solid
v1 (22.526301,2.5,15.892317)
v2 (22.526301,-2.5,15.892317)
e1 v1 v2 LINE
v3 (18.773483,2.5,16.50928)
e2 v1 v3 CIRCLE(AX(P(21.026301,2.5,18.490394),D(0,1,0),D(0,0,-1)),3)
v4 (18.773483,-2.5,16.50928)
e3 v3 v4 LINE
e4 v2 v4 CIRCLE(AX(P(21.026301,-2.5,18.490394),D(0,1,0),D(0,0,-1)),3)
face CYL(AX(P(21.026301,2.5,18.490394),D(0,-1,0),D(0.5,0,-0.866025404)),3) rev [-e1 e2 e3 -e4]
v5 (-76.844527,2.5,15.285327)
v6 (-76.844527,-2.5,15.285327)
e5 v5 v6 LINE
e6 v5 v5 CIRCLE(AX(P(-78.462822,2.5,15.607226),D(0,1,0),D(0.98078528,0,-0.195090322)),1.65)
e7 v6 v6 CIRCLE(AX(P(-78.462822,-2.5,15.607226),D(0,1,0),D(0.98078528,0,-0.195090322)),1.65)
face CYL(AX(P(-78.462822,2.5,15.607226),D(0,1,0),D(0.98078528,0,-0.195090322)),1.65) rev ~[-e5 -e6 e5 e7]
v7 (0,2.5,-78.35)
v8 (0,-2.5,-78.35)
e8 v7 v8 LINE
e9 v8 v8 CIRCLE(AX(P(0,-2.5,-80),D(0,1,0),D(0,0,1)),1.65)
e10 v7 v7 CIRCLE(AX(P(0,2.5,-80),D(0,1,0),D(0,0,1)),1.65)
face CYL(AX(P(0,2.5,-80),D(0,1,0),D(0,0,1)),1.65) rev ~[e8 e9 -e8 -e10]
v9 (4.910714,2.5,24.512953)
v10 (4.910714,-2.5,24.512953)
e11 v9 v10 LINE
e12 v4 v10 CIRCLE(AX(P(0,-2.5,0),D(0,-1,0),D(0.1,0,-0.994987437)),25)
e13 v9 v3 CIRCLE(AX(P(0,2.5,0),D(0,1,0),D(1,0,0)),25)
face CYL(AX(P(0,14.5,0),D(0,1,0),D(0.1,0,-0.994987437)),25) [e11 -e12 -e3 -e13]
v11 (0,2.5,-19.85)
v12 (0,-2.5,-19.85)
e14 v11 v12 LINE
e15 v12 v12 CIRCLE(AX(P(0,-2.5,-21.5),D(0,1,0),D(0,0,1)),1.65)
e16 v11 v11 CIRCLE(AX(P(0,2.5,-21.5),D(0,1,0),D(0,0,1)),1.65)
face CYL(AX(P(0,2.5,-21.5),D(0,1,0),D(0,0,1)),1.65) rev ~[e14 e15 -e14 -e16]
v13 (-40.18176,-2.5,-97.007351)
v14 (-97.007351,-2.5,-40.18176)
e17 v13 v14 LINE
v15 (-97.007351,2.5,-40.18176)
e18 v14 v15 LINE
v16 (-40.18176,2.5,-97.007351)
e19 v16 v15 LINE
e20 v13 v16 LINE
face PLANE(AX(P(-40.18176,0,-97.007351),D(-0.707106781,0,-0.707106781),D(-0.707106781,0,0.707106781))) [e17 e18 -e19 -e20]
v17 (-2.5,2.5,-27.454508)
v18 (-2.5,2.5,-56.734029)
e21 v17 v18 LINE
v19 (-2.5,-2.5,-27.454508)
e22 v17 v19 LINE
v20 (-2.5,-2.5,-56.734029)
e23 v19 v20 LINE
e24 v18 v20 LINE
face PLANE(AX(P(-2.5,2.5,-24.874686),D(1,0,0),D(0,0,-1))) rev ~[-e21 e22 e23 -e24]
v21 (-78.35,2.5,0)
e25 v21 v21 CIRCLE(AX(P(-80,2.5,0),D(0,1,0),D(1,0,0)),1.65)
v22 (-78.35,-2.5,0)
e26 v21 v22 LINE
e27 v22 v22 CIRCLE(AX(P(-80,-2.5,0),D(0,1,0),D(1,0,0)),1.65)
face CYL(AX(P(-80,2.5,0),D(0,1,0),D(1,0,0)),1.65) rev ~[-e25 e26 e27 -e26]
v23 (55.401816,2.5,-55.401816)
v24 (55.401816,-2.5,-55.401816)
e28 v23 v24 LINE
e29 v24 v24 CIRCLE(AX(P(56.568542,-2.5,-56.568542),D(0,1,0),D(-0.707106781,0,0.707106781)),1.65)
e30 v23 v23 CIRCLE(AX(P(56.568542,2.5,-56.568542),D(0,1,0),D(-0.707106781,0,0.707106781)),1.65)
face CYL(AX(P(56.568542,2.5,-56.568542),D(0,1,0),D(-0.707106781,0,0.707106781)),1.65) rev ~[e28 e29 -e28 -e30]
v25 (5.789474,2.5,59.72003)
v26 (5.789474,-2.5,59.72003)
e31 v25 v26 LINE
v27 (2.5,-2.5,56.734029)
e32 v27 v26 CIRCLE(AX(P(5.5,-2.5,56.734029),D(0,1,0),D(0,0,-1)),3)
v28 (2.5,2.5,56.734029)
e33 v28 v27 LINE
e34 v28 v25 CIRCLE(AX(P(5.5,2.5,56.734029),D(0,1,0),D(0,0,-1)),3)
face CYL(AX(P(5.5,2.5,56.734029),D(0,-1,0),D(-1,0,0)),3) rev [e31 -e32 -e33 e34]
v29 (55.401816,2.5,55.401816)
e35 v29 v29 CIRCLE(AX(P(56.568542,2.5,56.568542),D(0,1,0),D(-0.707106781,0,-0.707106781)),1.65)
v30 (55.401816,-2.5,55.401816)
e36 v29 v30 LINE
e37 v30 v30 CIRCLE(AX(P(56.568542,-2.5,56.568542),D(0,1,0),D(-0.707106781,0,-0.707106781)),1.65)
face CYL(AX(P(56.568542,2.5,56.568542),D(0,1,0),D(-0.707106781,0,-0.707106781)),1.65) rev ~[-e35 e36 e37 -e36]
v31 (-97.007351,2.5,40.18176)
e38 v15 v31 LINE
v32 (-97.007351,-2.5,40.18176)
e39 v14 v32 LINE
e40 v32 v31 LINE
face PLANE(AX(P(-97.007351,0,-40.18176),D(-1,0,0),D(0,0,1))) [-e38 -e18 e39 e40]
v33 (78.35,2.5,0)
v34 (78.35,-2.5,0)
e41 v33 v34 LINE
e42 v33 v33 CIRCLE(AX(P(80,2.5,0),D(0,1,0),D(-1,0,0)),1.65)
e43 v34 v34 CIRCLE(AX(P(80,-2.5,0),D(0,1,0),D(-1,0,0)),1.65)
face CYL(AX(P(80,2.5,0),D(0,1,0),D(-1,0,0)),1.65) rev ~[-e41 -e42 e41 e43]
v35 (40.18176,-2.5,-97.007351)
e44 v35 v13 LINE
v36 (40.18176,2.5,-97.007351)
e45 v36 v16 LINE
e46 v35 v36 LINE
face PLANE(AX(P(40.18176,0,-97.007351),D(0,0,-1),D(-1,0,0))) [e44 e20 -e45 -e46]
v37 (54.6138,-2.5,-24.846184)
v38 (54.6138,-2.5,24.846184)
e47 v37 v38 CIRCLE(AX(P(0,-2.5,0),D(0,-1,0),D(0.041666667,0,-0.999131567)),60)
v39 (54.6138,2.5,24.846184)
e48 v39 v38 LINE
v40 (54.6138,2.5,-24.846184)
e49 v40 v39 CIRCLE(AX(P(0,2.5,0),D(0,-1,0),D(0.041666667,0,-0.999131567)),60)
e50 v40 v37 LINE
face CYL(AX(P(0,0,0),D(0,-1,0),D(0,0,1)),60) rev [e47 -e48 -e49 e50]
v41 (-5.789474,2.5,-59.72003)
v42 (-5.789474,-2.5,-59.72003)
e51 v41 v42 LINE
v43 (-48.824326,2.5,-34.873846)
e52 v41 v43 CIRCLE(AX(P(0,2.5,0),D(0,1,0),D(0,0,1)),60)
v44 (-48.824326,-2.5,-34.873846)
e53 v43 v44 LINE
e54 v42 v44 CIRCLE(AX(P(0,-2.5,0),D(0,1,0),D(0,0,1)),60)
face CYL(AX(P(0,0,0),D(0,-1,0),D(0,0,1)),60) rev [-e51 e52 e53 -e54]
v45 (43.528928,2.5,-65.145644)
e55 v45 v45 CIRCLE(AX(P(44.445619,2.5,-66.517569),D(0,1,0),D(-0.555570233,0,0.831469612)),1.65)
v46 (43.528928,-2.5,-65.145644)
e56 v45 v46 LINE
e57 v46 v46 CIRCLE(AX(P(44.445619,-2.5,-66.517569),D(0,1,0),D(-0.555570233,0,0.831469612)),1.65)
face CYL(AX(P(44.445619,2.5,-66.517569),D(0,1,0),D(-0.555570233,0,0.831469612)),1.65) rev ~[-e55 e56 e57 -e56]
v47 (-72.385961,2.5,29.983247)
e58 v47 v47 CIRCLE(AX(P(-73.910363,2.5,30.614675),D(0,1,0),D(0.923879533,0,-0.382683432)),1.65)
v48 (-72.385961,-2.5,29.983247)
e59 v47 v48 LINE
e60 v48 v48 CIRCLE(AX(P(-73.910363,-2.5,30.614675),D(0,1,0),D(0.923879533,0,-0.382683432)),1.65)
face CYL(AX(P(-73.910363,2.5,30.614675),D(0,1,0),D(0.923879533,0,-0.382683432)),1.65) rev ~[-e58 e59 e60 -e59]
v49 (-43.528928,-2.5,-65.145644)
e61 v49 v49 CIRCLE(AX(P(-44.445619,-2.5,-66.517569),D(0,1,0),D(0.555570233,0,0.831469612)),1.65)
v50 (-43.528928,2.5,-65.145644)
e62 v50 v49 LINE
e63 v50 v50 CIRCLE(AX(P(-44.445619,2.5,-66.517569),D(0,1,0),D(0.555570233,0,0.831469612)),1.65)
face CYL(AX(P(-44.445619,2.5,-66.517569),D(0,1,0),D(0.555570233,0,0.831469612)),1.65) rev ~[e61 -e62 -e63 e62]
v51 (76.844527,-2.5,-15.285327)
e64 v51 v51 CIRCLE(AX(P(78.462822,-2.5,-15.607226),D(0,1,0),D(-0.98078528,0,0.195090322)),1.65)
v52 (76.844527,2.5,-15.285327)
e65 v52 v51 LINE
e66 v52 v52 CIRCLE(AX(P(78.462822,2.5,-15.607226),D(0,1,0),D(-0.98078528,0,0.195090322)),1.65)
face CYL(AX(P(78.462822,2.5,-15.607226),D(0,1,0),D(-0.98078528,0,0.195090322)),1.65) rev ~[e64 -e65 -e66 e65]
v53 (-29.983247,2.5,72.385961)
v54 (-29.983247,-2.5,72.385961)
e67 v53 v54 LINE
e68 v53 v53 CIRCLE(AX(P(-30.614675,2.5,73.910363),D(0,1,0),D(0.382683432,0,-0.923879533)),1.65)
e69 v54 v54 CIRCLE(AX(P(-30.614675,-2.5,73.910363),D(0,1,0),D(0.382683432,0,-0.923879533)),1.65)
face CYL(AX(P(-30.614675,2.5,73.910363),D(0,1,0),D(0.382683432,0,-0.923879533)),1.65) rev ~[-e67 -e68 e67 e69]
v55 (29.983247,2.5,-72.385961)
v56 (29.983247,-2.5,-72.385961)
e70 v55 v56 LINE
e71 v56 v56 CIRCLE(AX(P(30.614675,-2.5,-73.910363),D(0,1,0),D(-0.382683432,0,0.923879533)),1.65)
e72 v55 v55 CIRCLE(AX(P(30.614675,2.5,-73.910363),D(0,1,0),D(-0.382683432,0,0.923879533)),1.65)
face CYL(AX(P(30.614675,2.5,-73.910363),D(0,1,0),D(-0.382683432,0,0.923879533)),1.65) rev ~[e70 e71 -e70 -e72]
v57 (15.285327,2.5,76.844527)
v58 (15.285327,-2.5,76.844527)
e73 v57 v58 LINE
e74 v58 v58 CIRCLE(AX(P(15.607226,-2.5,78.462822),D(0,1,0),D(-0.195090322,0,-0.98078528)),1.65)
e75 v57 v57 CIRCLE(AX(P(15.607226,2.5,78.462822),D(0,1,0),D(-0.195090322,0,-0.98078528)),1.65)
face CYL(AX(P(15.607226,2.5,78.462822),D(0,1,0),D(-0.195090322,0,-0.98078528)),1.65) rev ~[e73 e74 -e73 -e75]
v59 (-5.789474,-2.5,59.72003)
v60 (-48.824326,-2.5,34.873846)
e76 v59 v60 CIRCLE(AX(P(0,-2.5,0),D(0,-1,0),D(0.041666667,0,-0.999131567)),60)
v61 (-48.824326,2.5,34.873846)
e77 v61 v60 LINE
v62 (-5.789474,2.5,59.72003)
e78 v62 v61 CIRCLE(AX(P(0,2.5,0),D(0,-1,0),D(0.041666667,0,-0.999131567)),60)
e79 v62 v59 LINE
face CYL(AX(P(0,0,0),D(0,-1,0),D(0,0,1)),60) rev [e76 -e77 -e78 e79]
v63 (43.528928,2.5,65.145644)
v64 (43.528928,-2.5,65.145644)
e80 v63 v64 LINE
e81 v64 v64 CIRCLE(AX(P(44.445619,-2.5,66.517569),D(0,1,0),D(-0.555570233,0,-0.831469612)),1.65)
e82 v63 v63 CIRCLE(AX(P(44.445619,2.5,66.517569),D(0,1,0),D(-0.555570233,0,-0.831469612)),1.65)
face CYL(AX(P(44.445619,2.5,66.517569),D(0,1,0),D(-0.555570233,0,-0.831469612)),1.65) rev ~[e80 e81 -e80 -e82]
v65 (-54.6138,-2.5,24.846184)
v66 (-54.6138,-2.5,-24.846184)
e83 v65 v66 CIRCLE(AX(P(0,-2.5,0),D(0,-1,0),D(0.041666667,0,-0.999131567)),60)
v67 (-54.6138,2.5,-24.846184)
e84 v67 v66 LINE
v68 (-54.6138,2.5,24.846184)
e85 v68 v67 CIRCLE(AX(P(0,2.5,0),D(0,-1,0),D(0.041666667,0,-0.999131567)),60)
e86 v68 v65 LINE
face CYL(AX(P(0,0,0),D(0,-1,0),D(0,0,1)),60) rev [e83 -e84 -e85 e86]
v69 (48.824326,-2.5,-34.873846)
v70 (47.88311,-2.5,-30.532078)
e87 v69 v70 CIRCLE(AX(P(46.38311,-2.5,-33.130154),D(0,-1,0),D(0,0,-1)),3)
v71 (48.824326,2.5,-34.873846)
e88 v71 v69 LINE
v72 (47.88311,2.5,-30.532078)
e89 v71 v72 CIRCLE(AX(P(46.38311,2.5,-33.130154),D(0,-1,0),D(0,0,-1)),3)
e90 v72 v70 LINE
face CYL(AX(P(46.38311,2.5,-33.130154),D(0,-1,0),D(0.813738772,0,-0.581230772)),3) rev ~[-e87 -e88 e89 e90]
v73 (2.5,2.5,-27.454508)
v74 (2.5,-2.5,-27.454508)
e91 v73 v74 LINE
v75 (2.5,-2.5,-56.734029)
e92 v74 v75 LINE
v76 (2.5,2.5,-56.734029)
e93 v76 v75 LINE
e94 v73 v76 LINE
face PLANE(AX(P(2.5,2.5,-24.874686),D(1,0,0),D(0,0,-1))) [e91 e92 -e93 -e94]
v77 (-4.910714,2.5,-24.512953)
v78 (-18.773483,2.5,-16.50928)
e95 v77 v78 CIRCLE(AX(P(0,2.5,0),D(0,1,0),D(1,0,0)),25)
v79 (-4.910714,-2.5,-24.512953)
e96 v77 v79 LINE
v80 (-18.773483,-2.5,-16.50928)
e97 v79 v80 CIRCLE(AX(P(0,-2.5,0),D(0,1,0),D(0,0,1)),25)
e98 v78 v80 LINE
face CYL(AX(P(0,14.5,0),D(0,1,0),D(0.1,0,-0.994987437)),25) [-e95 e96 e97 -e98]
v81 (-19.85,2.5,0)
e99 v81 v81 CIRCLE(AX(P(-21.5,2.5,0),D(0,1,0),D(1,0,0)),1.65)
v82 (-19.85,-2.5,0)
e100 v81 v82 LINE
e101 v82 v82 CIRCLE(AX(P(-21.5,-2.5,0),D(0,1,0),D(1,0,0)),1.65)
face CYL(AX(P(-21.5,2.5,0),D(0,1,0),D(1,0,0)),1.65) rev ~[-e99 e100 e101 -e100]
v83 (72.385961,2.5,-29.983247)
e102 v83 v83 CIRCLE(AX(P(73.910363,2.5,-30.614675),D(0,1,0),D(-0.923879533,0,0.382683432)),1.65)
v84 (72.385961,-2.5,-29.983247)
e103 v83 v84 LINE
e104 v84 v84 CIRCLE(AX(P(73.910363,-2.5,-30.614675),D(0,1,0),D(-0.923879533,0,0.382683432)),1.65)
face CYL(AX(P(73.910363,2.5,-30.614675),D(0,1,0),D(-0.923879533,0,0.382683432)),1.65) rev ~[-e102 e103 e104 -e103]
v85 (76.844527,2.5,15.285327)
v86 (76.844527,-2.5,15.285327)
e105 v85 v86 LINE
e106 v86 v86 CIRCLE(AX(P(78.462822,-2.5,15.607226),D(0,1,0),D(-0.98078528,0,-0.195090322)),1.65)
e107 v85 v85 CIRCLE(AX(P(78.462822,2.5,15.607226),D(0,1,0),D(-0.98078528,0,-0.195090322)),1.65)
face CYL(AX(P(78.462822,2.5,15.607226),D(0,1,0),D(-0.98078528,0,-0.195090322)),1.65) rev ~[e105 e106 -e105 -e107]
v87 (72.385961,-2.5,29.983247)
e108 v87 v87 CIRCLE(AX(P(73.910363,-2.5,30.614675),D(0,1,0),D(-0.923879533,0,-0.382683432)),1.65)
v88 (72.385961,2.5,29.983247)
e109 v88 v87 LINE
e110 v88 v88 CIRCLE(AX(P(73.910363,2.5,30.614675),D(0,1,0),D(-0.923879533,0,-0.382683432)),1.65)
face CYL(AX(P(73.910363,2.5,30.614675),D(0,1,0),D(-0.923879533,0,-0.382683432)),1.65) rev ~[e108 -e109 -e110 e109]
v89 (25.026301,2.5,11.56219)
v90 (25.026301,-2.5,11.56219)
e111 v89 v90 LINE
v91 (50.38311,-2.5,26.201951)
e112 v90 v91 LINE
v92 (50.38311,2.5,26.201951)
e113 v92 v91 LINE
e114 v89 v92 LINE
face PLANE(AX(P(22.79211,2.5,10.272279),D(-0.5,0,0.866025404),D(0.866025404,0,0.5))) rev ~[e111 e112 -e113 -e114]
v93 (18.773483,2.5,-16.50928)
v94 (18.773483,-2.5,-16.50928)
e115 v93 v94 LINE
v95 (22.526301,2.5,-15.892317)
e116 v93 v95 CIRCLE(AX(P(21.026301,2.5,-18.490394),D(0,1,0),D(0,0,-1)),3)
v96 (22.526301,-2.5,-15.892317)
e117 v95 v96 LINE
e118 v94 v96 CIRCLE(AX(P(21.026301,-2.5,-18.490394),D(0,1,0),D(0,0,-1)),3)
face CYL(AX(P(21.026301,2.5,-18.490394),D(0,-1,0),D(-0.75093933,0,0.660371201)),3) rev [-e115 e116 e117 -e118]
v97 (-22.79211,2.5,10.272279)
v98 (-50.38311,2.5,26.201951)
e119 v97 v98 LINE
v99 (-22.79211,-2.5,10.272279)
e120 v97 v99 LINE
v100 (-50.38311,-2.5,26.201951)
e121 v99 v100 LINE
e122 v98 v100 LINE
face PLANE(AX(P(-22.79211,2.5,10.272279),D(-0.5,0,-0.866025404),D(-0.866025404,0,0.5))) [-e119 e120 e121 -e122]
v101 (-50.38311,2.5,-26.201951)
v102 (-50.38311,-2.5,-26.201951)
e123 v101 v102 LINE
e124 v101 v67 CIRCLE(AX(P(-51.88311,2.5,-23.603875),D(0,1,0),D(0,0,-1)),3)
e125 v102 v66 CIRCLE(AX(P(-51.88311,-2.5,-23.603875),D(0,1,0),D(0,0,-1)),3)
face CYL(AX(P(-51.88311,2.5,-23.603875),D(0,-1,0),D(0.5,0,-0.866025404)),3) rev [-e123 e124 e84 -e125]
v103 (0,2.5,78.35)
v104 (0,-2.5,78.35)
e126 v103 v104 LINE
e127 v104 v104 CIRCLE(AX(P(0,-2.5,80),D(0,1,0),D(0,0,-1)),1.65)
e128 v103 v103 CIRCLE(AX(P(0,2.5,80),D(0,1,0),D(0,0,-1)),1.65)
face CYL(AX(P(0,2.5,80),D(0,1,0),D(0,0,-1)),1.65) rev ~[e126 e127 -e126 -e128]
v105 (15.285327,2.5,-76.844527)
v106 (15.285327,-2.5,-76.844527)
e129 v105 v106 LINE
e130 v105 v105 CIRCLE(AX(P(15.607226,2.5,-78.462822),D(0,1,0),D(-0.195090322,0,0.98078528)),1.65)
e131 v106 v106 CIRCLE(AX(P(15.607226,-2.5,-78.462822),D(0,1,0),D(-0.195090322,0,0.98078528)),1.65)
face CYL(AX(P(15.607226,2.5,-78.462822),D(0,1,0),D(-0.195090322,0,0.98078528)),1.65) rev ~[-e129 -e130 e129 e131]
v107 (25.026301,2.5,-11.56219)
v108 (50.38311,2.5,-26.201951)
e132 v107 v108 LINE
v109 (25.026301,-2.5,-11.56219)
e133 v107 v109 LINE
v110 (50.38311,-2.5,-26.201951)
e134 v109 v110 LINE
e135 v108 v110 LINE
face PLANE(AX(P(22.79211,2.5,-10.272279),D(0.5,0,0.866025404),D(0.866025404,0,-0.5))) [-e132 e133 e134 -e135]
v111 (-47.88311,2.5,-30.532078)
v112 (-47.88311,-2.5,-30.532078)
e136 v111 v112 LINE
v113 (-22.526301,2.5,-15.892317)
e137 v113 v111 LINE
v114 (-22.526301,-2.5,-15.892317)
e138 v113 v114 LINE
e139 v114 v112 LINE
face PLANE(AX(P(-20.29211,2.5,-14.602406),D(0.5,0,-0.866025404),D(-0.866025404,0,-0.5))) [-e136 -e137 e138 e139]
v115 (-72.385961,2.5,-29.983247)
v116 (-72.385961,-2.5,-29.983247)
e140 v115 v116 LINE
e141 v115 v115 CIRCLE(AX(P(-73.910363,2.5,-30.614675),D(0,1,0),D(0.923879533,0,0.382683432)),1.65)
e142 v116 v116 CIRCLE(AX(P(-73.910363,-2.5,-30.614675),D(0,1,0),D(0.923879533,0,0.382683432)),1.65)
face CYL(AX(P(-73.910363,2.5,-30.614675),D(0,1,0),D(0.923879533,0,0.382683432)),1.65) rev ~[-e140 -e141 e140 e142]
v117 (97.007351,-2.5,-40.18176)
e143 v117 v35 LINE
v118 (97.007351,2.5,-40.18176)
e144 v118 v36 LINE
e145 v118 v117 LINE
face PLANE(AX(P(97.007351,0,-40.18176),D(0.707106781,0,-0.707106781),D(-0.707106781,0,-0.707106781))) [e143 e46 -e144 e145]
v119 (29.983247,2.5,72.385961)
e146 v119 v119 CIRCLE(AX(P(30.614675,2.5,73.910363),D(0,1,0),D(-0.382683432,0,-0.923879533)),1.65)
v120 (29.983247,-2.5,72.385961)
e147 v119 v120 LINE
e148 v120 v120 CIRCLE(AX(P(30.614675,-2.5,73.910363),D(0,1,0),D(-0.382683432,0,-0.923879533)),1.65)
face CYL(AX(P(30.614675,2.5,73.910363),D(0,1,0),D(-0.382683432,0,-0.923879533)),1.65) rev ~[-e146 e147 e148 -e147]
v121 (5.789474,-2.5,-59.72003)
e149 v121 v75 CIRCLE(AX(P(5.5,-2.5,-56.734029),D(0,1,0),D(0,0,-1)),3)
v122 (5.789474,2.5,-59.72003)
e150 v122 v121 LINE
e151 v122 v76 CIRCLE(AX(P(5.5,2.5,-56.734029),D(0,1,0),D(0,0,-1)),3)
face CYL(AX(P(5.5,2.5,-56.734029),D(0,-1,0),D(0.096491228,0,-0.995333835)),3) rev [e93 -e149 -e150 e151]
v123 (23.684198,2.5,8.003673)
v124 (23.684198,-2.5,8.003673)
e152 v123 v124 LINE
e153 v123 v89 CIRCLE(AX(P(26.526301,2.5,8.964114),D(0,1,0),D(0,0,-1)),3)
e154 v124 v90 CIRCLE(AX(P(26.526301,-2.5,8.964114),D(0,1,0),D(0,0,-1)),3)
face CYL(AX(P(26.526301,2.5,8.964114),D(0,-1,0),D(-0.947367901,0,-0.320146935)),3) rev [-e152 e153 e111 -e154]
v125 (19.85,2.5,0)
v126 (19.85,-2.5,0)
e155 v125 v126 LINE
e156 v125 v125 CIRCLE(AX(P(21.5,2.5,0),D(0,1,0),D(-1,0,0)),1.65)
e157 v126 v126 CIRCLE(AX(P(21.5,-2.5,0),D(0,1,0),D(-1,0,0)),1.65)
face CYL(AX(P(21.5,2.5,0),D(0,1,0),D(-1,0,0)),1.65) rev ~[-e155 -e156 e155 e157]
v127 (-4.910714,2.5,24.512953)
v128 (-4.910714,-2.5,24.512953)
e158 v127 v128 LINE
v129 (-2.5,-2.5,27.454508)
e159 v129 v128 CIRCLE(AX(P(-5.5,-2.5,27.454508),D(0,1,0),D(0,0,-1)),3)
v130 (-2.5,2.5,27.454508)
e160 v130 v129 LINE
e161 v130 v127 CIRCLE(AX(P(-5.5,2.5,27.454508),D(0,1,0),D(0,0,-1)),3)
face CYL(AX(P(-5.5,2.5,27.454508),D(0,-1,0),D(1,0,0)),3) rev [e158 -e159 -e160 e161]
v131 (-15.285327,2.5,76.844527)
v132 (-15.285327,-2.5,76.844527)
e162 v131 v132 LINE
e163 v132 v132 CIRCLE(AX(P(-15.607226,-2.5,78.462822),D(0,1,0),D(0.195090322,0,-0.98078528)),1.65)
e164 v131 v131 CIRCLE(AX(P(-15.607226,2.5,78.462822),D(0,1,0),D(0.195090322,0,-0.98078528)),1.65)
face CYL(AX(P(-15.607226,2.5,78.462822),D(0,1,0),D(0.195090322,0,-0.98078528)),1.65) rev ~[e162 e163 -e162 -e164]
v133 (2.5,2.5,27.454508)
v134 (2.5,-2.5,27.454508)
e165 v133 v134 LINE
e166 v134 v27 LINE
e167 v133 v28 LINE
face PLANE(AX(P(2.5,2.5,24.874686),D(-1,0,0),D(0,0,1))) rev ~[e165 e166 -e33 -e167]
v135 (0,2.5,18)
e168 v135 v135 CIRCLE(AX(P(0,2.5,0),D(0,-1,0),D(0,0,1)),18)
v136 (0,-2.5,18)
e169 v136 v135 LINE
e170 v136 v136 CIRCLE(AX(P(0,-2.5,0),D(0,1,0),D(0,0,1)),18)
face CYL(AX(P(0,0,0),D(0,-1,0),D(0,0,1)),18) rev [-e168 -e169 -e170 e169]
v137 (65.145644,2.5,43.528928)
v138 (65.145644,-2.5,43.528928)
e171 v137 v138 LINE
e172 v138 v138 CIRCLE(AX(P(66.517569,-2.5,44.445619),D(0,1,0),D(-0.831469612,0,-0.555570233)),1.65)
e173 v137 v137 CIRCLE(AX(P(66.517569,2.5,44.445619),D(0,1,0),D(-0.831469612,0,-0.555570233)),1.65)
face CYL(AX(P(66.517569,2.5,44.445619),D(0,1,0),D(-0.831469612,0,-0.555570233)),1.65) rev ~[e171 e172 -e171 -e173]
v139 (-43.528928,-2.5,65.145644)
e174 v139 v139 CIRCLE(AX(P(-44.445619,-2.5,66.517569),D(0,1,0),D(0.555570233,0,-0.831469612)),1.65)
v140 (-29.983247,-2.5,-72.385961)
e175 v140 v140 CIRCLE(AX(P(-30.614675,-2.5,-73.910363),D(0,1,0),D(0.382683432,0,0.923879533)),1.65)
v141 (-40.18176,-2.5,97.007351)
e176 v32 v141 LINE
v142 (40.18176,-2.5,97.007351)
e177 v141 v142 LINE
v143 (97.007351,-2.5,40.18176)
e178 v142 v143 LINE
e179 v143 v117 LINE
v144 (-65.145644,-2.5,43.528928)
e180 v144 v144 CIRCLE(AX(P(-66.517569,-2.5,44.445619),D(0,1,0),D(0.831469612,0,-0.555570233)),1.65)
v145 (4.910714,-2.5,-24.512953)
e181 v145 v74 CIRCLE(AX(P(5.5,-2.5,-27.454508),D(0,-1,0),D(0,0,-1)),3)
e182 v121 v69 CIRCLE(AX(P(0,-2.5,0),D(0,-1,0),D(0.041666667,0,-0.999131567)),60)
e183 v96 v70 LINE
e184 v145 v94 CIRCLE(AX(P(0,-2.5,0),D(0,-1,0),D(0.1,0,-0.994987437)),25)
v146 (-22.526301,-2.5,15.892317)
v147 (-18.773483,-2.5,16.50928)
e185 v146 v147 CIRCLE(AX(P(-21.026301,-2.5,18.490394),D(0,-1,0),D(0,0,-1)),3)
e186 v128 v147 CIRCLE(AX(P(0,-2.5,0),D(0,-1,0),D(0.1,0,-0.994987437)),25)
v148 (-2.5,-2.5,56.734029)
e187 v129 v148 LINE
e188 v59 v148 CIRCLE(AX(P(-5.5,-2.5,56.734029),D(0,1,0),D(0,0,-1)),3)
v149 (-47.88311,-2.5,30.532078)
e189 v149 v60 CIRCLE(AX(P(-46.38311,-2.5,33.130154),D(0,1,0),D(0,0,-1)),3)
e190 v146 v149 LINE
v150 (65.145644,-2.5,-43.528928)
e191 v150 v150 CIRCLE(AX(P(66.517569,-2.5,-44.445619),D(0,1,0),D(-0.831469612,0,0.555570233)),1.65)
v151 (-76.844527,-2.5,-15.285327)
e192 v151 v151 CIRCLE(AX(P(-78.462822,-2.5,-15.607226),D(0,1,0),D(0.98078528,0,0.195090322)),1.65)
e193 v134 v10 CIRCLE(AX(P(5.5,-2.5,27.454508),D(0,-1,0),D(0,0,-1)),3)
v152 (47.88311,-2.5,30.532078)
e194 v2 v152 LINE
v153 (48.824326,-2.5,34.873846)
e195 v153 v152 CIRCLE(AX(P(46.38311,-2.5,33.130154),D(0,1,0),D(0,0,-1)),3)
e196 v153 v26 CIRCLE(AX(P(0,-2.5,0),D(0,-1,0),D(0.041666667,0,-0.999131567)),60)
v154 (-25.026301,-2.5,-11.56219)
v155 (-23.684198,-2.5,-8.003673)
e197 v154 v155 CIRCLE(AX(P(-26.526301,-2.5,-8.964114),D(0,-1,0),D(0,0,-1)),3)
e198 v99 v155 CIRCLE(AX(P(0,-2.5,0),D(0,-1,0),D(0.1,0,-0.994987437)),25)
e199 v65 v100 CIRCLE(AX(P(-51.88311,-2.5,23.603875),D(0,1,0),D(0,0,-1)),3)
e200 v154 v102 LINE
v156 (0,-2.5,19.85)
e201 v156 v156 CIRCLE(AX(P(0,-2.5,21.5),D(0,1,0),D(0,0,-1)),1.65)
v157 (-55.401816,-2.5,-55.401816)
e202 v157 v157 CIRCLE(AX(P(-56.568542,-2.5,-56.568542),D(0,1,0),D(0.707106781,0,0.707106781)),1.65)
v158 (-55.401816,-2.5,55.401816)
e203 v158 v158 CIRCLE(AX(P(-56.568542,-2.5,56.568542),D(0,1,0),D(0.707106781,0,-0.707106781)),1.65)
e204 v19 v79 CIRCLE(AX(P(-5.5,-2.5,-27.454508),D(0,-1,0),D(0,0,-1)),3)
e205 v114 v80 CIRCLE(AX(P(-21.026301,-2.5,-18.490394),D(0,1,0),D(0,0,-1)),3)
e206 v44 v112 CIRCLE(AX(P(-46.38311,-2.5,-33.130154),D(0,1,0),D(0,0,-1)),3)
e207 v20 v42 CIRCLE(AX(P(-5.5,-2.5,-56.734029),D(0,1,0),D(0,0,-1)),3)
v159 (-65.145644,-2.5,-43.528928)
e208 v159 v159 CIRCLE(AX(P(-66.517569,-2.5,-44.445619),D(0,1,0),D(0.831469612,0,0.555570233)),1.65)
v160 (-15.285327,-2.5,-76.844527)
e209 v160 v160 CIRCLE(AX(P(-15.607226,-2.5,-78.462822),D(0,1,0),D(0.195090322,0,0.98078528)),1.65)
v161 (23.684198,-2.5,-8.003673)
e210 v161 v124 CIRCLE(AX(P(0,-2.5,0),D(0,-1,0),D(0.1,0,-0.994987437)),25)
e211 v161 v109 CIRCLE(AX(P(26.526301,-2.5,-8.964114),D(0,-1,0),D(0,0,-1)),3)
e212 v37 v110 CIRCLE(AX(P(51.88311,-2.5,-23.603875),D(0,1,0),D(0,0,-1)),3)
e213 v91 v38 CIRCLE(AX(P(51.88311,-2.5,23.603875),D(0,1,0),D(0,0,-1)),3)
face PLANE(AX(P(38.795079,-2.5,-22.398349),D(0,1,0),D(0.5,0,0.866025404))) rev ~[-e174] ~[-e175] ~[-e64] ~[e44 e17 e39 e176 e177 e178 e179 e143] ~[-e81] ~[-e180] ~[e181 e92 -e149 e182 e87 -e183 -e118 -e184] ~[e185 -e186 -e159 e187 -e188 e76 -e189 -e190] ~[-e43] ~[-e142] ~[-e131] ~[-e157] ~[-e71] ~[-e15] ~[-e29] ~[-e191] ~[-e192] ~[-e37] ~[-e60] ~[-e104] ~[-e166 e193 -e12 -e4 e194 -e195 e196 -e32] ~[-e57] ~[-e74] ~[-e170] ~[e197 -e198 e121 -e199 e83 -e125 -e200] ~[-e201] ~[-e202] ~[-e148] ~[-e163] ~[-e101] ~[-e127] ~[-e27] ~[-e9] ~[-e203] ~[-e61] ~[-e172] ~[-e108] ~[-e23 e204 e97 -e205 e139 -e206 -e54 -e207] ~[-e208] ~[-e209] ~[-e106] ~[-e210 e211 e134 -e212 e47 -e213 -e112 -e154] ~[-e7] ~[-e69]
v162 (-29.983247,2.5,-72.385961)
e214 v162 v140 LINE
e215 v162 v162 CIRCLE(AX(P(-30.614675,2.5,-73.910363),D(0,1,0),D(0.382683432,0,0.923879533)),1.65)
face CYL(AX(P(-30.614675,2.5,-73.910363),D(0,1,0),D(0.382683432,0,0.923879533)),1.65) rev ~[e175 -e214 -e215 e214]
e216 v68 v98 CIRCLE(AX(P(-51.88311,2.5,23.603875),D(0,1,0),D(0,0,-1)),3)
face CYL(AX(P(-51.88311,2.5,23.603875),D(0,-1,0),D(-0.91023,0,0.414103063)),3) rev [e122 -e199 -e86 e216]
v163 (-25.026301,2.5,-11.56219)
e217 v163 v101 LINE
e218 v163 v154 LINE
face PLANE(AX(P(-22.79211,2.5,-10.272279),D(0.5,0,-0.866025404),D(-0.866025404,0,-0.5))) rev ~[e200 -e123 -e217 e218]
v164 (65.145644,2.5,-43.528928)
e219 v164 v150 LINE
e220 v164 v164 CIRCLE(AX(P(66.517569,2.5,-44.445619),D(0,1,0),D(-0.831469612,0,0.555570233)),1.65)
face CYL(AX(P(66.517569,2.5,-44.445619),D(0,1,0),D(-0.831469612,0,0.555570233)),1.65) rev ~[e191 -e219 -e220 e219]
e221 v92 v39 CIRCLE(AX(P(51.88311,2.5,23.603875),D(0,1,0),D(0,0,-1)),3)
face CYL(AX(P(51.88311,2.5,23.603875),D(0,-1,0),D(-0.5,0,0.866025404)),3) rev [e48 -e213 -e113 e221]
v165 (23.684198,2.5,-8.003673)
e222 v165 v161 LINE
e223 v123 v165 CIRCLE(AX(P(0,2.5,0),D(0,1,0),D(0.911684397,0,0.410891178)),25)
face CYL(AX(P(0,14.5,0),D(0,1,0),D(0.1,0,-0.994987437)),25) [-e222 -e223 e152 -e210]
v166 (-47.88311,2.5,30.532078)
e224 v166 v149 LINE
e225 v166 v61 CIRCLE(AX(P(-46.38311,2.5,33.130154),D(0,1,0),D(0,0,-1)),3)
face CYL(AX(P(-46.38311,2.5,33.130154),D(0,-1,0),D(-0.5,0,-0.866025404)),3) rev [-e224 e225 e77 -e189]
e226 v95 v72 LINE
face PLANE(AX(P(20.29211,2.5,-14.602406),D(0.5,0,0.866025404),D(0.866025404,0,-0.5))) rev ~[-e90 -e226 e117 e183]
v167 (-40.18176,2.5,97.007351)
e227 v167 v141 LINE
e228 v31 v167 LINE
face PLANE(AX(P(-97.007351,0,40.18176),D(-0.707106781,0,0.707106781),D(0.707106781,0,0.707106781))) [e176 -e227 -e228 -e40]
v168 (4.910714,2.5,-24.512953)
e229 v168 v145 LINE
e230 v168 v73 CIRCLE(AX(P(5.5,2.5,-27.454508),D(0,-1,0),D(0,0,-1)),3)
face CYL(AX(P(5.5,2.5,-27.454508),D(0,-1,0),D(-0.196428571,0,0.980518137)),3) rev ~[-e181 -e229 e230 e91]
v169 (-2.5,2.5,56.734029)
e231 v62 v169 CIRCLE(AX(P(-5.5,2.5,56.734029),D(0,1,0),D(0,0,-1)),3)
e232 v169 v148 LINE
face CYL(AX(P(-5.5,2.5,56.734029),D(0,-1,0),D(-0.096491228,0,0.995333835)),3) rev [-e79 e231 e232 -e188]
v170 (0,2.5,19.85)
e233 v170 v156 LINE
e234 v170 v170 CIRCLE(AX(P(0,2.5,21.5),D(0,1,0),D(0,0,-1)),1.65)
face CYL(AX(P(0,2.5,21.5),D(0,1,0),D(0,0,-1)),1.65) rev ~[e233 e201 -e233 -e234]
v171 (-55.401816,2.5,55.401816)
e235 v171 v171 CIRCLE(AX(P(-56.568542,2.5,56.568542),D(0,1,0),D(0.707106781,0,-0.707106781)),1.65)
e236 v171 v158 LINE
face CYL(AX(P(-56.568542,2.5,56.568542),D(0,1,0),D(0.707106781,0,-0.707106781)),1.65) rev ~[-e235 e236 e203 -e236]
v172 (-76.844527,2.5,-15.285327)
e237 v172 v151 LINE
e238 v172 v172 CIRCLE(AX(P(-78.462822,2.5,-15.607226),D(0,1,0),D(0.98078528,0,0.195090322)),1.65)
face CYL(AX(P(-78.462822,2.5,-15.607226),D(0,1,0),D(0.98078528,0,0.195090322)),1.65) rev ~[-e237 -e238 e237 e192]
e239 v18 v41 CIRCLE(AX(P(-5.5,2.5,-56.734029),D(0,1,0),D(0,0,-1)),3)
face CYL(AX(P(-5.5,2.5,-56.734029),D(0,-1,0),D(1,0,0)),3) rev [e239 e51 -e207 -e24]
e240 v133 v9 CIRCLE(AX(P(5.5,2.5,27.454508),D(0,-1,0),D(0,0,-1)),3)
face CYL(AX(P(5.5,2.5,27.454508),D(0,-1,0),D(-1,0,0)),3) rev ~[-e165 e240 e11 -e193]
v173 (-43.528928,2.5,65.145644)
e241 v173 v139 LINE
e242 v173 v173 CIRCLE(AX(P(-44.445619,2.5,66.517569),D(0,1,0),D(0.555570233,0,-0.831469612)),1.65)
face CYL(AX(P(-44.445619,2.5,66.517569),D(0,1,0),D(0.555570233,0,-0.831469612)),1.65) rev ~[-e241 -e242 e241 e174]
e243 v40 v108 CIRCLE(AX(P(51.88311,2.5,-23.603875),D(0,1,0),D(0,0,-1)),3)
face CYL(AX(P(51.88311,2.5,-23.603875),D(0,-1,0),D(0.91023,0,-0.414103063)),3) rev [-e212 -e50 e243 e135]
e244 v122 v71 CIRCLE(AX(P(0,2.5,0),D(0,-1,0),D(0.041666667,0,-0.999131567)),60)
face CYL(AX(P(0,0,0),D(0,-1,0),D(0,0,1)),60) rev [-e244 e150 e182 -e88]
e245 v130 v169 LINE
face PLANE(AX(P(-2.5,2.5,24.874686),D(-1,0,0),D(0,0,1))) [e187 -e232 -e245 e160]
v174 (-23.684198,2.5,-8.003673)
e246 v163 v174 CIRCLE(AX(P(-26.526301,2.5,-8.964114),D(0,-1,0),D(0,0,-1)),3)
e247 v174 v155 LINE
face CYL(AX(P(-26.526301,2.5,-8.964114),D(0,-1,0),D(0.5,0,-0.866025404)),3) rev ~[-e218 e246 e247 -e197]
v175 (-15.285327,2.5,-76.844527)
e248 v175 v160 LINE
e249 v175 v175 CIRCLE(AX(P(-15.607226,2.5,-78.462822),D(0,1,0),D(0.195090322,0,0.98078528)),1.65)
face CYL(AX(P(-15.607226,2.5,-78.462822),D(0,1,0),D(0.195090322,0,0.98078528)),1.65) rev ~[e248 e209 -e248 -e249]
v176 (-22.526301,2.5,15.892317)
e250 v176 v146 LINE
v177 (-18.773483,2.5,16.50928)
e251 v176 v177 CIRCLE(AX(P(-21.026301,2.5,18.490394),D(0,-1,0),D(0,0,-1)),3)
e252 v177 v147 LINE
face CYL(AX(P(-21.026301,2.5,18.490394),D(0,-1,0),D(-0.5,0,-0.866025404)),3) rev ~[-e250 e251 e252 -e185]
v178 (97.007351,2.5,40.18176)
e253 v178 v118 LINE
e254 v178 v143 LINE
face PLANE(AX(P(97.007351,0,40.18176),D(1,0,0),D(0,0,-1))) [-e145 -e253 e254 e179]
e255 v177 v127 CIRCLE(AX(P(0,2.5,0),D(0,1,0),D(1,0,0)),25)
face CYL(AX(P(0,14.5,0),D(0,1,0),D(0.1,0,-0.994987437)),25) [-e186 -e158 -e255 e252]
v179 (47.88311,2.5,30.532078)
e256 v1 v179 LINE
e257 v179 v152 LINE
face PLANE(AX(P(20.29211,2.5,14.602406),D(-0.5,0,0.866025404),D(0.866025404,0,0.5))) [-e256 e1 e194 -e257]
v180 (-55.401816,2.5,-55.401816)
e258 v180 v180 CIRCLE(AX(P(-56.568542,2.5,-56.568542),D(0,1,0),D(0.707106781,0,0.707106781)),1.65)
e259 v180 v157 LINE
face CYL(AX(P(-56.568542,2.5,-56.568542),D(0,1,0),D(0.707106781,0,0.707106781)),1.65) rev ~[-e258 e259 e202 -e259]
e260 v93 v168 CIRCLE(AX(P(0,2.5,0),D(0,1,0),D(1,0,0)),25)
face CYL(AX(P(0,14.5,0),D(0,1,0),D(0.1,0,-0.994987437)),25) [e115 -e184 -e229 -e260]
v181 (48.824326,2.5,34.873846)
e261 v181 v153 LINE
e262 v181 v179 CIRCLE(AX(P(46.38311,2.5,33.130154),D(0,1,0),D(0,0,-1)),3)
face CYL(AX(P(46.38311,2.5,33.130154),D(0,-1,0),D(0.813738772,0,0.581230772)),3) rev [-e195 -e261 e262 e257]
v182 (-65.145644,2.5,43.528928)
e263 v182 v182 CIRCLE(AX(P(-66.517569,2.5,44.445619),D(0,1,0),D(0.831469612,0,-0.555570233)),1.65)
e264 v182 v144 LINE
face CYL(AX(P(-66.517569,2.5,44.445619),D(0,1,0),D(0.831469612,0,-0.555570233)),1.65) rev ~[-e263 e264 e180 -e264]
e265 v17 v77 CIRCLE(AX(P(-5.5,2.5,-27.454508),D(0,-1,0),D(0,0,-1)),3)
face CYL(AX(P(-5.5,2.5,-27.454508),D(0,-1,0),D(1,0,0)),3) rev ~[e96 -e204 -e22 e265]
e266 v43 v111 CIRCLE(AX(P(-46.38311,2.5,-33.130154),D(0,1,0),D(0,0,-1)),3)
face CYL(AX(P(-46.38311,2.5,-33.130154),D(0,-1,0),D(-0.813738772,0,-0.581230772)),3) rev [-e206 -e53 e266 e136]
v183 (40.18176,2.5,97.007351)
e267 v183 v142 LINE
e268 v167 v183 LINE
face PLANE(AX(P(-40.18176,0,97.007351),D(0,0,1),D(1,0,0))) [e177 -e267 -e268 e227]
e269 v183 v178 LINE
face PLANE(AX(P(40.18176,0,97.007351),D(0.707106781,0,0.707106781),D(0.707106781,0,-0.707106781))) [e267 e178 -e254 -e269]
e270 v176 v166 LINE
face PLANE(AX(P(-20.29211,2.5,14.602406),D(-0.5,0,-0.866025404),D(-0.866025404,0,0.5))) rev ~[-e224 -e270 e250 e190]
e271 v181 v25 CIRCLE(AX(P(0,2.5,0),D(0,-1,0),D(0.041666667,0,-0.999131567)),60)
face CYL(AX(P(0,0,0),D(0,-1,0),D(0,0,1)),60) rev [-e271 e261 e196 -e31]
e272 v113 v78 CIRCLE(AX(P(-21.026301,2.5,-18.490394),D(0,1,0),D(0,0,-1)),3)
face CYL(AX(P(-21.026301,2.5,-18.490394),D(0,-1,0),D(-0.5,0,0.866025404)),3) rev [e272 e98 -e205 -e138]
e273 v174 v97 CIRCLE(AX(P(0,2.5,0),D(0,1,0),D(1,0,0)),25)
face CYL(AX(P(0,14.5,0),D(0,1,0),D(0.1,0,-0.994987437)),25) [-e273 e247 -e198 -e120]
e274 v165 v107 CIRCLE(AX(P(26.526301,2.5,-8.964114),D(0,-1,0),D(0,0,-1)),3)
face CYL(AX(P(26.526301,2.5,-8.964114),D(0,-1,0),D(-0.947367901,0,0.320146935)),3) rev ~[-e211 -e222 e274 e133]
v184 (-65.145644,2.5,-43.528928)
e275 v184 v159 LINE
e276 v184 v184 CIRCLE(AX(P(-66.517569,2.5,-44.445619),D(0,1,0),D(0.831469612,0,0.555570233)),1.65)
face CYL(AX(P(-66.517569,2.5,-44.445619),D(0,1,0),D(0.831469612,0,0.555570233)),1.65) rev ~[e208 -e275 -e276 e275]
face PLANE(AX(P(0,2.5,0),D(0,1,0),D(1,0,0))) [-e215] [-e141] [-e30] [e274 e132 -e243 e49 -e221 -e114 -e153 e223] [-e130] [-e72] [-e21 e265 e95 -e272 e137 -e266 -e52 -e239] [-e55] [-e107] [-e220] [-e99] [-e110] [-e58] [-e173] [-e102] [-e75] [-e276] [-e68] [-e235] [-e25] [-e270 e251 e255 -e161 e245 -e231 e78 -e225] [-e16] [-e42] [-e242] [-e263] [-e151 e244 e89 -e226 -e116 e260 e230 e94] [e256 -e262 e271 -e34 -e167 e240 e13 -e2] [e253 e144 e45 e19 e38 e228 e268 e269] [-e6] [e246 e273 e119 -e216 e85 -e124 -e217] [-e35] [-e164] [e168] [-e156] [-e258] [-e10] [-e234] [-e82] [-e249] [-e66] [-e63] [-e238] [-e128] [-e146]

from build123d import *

# Parameters (mm, degrees)
SKETCH_1_R               = 25
SKETCH_1_R_2             = 18
EXTRUDE_1_DEPTH          = 2.5
SKETCH_1_R_3             = 60
EXTRUDE_1_2_DEPTH        = 2.5
SKETCH_8_W               = 5
SKETCH_8_H               = 39.844025058
EXTRUDE_2_DEPTH          = 5
PATTERN_CIRCULAR_3_COUNT = 6
EXTRUDE_START            = 12
SKETCH_9_R               = 25
SKETCH_9_R_2             = 18
EXTRUDE_3_DEPTH          = 12
SKETCH_11_R              = 1.65
CUT_EXTRUDE_3_DEPTH      = 8
PATTERN_CIRCULAR_5_COUNT = 32
SKETCH_12_R              = 2.2
CUT_EXTRUDE_4_DEPTH      = 45
CUT_EXTRUDE_START        = -24
SKETCH_13_R              = 4
CUT_EXTRUDE_5_DEPTH      = 45
PATTERN_CIRCULAR_6_COUNT = 4
SKETCH_14_R              = 25
CUT_EXTRUDE_6_DEPTH      = 12
FILLET_1_R               = 3
SKETCH_15_R              = 1.65
CUT_EXTRUDE_7_DEPTH      = 10
PATTERN_CIRCULAR_7_COUNT = 4


with BuildPart() as part:
    # 草图1 → 凸台-拉伸1 (new, symmetric)
    with BuildSketch(Plane(origin=(0, 0, 0), x_dir=(1, 0, 0), z_dir=(0, 1, 0))):
        with Locations(Location((0, 0, 0), (0, 0, 270))):
            Circle(SKETCH_1_R)
        with Locations(Location((0, 0, 0), (0, 0, 270))):
            Circle(SKETCH_1_R_2, mode=Mode.SUBTRACT)
    extrude(amount=EXTRUDE_1_DEPTH, both=True)



with BuildPart() as body_2:
    # 草图1 → Extrude 1 2 (new, symmetric)
    with BuildSketch(Plane(origin=(0, 0, 0), x_dir=(1, 0, 0), z_dir=(0, 1, 0))):
        Polygon((97.007350914, 40.181760398), (40.181760398, 97.007350914), (-40.181760398, 97.007350914), (-97.007350914, 40.181760398), (-97.007350914, -40.181760398), (-40.181760398, -97.007350914), (40.181760398, -97.007350914), (97.007350914, -40.181760398), align=None)
        with Locations(Location((0, 0, 0), (0, 0, 270))):
            Circle(SKETCH_1_R_3, mode=Mode.SUBTRACT)
    extrude(amount=EXTRUDE_1_2_DEPTH, both=True)


with BuildPart() as part_1:
    add(part.part)

    add(body_2.part)  # 凸台-拉伸2 merges body 2
    # 草图8 → 凸台-拉伸2 (add)
    with BuildSketch(Plane(origin=(0, 2.5, 0), x_dir=(1, 0, 0), z_dir=(0, 1, 0))):
        with Locations((0, 44.796698457)):
            Rectangle(SKETCH_8_W, SKETCH_8_H)
    extrude_2 = extrude(amount=-EXTRUDE_2_DEPTH)

    # 阵列(圆周)3: 凸台-拉伸2 ×6 about axis
    pattern_circular_3_axis = Axis((0, 0, 0), (0, 1, 0))
    for i in range(1, PATTERN_CIRCULAR_3_COUNT):
        add(extrude_2.rotate(pattern_circular_3_axis, i * 360 / PATTERN_CIRCULAR_3_COUNT))

    # 草图9 → 凸台-拉伸3 (add)
    with BuildSketch(Plane(origin=(0, 2.5, 0), x_dir=(1, 0, 0), z_dir=(0, 1, 0)).offset(EXTRUDE_START)):
        with Locations(Location((0, 0, 0), (0, 0, 84.260829523))):
            Circle(SKETCH_9_R)
        with Locations(Location((0, 0, 0), (0, 0, 270))):
            Circle(SKETCH_9_R_2, mode=Mode.SUBTRACT)
    extrude(amount=-EXTRUDE_3_DEPTH)

    # 草图11 → 切除-拉伸3 (cut)
    with BuildSketch(Plane(origin=(0, 2.5, 0), x_dir=(1, 0, 0), z_dir=(0, 1, 0))):
        with Locations(Location((0, 80, 0), (0, 0, 270))):
            Circle(SKETCH_11_R)
    cut_extrude_3 = extrude(amount=-CUT_EXTRUDE_3_DEPTH, mode=Mode.SUBTRACT)

    # 阵列(圆周)5: 切除-拉伸3 ×32 about axis
    pattern_circular_5_axis = Axis((0, 0, 0), (0, 1, 0))
    for i in range(1, PATTERN_CIRCULAR_5_COUNT):
        add(cut_extrude_3.rotate(pattern_circular_5_axis, i * 360 / PATTERN_CIRCULAR_5_COUNT), mode=Mode.SUBTRACT)

    # 草图12 → 切除-拉伸4 (cut)
    with BuildSketch(Plane.XY):
        with Locations(Location((0, 9.5, 0), (0, 0, 90))):
            Circle(SKETCH_12_R)
    cut_extrude_4 = extrude(amount=-CUT_EXTRUDE_4_DEPTH, mode=Mode.SUBTRACT)

    # 草图13 → 切除-拉伸5 (cut)
    with BuildSketch(Plane.XY.offset(CUT_EXTRUDE_START)):
        with Locations((0, 9.5)):
            Circle(SKETCH_13_R)
    cut_extrude_5 = extrude(amount=-CUT_EXTRUDE_5_DEPTH, mode=Mode.SUBTRACT)

    # 阵列(圆周)6: 切除-拉伸4, 切除-拉伸5 ×4 about axis
    pattern_circular_6_axis = Axis((0, 0, 0), (0, 1, 0))
    add([cut_extrude_4.rotate(pattern_circular_6_axis, i * 360 / PATTERN_CIRCULAR_6_COUNT) for i in range(1, PATTERN_CIRCULAR_6_COUNT)], mode=Mode.SUBTRACT)
    add([cut_extrude_5.rotate(pattern_circular_6_axis, i * 360 / PATTERN_CIRCULAR_6_COUNT) for i in range(1, PATTERN_CIRCULAR_6_COUNT)], mode=Mode.SUBTRACT)

    # 草图14 → 切除-拉伸6 (cut)
    with BuildSketch(Plane(origin=(0, 14.5, 0), x_dir=(1, 0, 0), z_dir=(0, 1, 0))):
        Circle(SKETCH_14_R)
    extrude(amount=-CUT_EXTRUDE_6_DEPTH, mode=Mode.SUBTRACT)

    # 圆角1
    fillet_1_edges = [part_1.edges().sort_by_distance(p)[0] for p in [
        (2.5, 0, 59.947894041),
        (2.5, 0, 24.874685928),
        (-2.5, 0, 59.947894041),
        (-2.5, 0, 24.874685928),
        (-50.666399143, 0, 32.13901053),
        (-20.292109925, 0, 14.602406473),
        (-53.166399143, 0, 27.808883511),
        (-53.166399143, 0, -27.808883511),
        (-22.792109925, 0, -10.272279454),
        (-50.666399143, 0, -32.13901053),
        (-20.292109925, 0, -14.602406473),
        (-2.5, 0, -59.947894041),
        (-2.5, 0, -24.874685928),
        (2.5, 0, -59.947894041),
        (2.5, 0, -24.874685928),
        (50.666399143, 0, -32.13901053),
        (20.292109925, 0, -14.602406473),
        (53.166399143, 0, -27.808883511),
        (22.792109925, 0, -10.272279454),
        (53.166399143, 0, 27.808883511),
        (22.792109925, 0, 10.272279454),
        (50.666399143, 0, 32.13901053),
        (20.292109925, 0, 14.602406473),
    ]]
    fillet(fillet_1_edges, radius=FILLET_1_R)

    # 草图15 → 切除-拉伸7 (cut)
    with BuildSketch(Plane(origin=(0, 2.5, 0), x_dir=(1, 0, 0), z_dir=(0, 1, 0))):
        with Locations(Location((0, 21.5, 0), (0, 0, 270))):
            Circle(SKETCH_15_R)
    cut_extrude_7 = extrude(amount=-CUT_EXTRUDE_7_DEPTH, mode=Mode.SUBTRACT)

    # 阵列(圆周)7: 切除-拉伸7 ×4 about axis
    pattern_circular_7_axis = Axis((0, 0, 0), (0, 1, 0))
    for i in range(1, PATTERN_CIRCULAR_7_COUNT):
        add(cut_extrude_7.rotate(pattern_circular_7_axis, i * 360 / PATTERN_CIRCULAR_7_COUNT), mode=Mode.SUBTRACT)


solid = part_1.part
